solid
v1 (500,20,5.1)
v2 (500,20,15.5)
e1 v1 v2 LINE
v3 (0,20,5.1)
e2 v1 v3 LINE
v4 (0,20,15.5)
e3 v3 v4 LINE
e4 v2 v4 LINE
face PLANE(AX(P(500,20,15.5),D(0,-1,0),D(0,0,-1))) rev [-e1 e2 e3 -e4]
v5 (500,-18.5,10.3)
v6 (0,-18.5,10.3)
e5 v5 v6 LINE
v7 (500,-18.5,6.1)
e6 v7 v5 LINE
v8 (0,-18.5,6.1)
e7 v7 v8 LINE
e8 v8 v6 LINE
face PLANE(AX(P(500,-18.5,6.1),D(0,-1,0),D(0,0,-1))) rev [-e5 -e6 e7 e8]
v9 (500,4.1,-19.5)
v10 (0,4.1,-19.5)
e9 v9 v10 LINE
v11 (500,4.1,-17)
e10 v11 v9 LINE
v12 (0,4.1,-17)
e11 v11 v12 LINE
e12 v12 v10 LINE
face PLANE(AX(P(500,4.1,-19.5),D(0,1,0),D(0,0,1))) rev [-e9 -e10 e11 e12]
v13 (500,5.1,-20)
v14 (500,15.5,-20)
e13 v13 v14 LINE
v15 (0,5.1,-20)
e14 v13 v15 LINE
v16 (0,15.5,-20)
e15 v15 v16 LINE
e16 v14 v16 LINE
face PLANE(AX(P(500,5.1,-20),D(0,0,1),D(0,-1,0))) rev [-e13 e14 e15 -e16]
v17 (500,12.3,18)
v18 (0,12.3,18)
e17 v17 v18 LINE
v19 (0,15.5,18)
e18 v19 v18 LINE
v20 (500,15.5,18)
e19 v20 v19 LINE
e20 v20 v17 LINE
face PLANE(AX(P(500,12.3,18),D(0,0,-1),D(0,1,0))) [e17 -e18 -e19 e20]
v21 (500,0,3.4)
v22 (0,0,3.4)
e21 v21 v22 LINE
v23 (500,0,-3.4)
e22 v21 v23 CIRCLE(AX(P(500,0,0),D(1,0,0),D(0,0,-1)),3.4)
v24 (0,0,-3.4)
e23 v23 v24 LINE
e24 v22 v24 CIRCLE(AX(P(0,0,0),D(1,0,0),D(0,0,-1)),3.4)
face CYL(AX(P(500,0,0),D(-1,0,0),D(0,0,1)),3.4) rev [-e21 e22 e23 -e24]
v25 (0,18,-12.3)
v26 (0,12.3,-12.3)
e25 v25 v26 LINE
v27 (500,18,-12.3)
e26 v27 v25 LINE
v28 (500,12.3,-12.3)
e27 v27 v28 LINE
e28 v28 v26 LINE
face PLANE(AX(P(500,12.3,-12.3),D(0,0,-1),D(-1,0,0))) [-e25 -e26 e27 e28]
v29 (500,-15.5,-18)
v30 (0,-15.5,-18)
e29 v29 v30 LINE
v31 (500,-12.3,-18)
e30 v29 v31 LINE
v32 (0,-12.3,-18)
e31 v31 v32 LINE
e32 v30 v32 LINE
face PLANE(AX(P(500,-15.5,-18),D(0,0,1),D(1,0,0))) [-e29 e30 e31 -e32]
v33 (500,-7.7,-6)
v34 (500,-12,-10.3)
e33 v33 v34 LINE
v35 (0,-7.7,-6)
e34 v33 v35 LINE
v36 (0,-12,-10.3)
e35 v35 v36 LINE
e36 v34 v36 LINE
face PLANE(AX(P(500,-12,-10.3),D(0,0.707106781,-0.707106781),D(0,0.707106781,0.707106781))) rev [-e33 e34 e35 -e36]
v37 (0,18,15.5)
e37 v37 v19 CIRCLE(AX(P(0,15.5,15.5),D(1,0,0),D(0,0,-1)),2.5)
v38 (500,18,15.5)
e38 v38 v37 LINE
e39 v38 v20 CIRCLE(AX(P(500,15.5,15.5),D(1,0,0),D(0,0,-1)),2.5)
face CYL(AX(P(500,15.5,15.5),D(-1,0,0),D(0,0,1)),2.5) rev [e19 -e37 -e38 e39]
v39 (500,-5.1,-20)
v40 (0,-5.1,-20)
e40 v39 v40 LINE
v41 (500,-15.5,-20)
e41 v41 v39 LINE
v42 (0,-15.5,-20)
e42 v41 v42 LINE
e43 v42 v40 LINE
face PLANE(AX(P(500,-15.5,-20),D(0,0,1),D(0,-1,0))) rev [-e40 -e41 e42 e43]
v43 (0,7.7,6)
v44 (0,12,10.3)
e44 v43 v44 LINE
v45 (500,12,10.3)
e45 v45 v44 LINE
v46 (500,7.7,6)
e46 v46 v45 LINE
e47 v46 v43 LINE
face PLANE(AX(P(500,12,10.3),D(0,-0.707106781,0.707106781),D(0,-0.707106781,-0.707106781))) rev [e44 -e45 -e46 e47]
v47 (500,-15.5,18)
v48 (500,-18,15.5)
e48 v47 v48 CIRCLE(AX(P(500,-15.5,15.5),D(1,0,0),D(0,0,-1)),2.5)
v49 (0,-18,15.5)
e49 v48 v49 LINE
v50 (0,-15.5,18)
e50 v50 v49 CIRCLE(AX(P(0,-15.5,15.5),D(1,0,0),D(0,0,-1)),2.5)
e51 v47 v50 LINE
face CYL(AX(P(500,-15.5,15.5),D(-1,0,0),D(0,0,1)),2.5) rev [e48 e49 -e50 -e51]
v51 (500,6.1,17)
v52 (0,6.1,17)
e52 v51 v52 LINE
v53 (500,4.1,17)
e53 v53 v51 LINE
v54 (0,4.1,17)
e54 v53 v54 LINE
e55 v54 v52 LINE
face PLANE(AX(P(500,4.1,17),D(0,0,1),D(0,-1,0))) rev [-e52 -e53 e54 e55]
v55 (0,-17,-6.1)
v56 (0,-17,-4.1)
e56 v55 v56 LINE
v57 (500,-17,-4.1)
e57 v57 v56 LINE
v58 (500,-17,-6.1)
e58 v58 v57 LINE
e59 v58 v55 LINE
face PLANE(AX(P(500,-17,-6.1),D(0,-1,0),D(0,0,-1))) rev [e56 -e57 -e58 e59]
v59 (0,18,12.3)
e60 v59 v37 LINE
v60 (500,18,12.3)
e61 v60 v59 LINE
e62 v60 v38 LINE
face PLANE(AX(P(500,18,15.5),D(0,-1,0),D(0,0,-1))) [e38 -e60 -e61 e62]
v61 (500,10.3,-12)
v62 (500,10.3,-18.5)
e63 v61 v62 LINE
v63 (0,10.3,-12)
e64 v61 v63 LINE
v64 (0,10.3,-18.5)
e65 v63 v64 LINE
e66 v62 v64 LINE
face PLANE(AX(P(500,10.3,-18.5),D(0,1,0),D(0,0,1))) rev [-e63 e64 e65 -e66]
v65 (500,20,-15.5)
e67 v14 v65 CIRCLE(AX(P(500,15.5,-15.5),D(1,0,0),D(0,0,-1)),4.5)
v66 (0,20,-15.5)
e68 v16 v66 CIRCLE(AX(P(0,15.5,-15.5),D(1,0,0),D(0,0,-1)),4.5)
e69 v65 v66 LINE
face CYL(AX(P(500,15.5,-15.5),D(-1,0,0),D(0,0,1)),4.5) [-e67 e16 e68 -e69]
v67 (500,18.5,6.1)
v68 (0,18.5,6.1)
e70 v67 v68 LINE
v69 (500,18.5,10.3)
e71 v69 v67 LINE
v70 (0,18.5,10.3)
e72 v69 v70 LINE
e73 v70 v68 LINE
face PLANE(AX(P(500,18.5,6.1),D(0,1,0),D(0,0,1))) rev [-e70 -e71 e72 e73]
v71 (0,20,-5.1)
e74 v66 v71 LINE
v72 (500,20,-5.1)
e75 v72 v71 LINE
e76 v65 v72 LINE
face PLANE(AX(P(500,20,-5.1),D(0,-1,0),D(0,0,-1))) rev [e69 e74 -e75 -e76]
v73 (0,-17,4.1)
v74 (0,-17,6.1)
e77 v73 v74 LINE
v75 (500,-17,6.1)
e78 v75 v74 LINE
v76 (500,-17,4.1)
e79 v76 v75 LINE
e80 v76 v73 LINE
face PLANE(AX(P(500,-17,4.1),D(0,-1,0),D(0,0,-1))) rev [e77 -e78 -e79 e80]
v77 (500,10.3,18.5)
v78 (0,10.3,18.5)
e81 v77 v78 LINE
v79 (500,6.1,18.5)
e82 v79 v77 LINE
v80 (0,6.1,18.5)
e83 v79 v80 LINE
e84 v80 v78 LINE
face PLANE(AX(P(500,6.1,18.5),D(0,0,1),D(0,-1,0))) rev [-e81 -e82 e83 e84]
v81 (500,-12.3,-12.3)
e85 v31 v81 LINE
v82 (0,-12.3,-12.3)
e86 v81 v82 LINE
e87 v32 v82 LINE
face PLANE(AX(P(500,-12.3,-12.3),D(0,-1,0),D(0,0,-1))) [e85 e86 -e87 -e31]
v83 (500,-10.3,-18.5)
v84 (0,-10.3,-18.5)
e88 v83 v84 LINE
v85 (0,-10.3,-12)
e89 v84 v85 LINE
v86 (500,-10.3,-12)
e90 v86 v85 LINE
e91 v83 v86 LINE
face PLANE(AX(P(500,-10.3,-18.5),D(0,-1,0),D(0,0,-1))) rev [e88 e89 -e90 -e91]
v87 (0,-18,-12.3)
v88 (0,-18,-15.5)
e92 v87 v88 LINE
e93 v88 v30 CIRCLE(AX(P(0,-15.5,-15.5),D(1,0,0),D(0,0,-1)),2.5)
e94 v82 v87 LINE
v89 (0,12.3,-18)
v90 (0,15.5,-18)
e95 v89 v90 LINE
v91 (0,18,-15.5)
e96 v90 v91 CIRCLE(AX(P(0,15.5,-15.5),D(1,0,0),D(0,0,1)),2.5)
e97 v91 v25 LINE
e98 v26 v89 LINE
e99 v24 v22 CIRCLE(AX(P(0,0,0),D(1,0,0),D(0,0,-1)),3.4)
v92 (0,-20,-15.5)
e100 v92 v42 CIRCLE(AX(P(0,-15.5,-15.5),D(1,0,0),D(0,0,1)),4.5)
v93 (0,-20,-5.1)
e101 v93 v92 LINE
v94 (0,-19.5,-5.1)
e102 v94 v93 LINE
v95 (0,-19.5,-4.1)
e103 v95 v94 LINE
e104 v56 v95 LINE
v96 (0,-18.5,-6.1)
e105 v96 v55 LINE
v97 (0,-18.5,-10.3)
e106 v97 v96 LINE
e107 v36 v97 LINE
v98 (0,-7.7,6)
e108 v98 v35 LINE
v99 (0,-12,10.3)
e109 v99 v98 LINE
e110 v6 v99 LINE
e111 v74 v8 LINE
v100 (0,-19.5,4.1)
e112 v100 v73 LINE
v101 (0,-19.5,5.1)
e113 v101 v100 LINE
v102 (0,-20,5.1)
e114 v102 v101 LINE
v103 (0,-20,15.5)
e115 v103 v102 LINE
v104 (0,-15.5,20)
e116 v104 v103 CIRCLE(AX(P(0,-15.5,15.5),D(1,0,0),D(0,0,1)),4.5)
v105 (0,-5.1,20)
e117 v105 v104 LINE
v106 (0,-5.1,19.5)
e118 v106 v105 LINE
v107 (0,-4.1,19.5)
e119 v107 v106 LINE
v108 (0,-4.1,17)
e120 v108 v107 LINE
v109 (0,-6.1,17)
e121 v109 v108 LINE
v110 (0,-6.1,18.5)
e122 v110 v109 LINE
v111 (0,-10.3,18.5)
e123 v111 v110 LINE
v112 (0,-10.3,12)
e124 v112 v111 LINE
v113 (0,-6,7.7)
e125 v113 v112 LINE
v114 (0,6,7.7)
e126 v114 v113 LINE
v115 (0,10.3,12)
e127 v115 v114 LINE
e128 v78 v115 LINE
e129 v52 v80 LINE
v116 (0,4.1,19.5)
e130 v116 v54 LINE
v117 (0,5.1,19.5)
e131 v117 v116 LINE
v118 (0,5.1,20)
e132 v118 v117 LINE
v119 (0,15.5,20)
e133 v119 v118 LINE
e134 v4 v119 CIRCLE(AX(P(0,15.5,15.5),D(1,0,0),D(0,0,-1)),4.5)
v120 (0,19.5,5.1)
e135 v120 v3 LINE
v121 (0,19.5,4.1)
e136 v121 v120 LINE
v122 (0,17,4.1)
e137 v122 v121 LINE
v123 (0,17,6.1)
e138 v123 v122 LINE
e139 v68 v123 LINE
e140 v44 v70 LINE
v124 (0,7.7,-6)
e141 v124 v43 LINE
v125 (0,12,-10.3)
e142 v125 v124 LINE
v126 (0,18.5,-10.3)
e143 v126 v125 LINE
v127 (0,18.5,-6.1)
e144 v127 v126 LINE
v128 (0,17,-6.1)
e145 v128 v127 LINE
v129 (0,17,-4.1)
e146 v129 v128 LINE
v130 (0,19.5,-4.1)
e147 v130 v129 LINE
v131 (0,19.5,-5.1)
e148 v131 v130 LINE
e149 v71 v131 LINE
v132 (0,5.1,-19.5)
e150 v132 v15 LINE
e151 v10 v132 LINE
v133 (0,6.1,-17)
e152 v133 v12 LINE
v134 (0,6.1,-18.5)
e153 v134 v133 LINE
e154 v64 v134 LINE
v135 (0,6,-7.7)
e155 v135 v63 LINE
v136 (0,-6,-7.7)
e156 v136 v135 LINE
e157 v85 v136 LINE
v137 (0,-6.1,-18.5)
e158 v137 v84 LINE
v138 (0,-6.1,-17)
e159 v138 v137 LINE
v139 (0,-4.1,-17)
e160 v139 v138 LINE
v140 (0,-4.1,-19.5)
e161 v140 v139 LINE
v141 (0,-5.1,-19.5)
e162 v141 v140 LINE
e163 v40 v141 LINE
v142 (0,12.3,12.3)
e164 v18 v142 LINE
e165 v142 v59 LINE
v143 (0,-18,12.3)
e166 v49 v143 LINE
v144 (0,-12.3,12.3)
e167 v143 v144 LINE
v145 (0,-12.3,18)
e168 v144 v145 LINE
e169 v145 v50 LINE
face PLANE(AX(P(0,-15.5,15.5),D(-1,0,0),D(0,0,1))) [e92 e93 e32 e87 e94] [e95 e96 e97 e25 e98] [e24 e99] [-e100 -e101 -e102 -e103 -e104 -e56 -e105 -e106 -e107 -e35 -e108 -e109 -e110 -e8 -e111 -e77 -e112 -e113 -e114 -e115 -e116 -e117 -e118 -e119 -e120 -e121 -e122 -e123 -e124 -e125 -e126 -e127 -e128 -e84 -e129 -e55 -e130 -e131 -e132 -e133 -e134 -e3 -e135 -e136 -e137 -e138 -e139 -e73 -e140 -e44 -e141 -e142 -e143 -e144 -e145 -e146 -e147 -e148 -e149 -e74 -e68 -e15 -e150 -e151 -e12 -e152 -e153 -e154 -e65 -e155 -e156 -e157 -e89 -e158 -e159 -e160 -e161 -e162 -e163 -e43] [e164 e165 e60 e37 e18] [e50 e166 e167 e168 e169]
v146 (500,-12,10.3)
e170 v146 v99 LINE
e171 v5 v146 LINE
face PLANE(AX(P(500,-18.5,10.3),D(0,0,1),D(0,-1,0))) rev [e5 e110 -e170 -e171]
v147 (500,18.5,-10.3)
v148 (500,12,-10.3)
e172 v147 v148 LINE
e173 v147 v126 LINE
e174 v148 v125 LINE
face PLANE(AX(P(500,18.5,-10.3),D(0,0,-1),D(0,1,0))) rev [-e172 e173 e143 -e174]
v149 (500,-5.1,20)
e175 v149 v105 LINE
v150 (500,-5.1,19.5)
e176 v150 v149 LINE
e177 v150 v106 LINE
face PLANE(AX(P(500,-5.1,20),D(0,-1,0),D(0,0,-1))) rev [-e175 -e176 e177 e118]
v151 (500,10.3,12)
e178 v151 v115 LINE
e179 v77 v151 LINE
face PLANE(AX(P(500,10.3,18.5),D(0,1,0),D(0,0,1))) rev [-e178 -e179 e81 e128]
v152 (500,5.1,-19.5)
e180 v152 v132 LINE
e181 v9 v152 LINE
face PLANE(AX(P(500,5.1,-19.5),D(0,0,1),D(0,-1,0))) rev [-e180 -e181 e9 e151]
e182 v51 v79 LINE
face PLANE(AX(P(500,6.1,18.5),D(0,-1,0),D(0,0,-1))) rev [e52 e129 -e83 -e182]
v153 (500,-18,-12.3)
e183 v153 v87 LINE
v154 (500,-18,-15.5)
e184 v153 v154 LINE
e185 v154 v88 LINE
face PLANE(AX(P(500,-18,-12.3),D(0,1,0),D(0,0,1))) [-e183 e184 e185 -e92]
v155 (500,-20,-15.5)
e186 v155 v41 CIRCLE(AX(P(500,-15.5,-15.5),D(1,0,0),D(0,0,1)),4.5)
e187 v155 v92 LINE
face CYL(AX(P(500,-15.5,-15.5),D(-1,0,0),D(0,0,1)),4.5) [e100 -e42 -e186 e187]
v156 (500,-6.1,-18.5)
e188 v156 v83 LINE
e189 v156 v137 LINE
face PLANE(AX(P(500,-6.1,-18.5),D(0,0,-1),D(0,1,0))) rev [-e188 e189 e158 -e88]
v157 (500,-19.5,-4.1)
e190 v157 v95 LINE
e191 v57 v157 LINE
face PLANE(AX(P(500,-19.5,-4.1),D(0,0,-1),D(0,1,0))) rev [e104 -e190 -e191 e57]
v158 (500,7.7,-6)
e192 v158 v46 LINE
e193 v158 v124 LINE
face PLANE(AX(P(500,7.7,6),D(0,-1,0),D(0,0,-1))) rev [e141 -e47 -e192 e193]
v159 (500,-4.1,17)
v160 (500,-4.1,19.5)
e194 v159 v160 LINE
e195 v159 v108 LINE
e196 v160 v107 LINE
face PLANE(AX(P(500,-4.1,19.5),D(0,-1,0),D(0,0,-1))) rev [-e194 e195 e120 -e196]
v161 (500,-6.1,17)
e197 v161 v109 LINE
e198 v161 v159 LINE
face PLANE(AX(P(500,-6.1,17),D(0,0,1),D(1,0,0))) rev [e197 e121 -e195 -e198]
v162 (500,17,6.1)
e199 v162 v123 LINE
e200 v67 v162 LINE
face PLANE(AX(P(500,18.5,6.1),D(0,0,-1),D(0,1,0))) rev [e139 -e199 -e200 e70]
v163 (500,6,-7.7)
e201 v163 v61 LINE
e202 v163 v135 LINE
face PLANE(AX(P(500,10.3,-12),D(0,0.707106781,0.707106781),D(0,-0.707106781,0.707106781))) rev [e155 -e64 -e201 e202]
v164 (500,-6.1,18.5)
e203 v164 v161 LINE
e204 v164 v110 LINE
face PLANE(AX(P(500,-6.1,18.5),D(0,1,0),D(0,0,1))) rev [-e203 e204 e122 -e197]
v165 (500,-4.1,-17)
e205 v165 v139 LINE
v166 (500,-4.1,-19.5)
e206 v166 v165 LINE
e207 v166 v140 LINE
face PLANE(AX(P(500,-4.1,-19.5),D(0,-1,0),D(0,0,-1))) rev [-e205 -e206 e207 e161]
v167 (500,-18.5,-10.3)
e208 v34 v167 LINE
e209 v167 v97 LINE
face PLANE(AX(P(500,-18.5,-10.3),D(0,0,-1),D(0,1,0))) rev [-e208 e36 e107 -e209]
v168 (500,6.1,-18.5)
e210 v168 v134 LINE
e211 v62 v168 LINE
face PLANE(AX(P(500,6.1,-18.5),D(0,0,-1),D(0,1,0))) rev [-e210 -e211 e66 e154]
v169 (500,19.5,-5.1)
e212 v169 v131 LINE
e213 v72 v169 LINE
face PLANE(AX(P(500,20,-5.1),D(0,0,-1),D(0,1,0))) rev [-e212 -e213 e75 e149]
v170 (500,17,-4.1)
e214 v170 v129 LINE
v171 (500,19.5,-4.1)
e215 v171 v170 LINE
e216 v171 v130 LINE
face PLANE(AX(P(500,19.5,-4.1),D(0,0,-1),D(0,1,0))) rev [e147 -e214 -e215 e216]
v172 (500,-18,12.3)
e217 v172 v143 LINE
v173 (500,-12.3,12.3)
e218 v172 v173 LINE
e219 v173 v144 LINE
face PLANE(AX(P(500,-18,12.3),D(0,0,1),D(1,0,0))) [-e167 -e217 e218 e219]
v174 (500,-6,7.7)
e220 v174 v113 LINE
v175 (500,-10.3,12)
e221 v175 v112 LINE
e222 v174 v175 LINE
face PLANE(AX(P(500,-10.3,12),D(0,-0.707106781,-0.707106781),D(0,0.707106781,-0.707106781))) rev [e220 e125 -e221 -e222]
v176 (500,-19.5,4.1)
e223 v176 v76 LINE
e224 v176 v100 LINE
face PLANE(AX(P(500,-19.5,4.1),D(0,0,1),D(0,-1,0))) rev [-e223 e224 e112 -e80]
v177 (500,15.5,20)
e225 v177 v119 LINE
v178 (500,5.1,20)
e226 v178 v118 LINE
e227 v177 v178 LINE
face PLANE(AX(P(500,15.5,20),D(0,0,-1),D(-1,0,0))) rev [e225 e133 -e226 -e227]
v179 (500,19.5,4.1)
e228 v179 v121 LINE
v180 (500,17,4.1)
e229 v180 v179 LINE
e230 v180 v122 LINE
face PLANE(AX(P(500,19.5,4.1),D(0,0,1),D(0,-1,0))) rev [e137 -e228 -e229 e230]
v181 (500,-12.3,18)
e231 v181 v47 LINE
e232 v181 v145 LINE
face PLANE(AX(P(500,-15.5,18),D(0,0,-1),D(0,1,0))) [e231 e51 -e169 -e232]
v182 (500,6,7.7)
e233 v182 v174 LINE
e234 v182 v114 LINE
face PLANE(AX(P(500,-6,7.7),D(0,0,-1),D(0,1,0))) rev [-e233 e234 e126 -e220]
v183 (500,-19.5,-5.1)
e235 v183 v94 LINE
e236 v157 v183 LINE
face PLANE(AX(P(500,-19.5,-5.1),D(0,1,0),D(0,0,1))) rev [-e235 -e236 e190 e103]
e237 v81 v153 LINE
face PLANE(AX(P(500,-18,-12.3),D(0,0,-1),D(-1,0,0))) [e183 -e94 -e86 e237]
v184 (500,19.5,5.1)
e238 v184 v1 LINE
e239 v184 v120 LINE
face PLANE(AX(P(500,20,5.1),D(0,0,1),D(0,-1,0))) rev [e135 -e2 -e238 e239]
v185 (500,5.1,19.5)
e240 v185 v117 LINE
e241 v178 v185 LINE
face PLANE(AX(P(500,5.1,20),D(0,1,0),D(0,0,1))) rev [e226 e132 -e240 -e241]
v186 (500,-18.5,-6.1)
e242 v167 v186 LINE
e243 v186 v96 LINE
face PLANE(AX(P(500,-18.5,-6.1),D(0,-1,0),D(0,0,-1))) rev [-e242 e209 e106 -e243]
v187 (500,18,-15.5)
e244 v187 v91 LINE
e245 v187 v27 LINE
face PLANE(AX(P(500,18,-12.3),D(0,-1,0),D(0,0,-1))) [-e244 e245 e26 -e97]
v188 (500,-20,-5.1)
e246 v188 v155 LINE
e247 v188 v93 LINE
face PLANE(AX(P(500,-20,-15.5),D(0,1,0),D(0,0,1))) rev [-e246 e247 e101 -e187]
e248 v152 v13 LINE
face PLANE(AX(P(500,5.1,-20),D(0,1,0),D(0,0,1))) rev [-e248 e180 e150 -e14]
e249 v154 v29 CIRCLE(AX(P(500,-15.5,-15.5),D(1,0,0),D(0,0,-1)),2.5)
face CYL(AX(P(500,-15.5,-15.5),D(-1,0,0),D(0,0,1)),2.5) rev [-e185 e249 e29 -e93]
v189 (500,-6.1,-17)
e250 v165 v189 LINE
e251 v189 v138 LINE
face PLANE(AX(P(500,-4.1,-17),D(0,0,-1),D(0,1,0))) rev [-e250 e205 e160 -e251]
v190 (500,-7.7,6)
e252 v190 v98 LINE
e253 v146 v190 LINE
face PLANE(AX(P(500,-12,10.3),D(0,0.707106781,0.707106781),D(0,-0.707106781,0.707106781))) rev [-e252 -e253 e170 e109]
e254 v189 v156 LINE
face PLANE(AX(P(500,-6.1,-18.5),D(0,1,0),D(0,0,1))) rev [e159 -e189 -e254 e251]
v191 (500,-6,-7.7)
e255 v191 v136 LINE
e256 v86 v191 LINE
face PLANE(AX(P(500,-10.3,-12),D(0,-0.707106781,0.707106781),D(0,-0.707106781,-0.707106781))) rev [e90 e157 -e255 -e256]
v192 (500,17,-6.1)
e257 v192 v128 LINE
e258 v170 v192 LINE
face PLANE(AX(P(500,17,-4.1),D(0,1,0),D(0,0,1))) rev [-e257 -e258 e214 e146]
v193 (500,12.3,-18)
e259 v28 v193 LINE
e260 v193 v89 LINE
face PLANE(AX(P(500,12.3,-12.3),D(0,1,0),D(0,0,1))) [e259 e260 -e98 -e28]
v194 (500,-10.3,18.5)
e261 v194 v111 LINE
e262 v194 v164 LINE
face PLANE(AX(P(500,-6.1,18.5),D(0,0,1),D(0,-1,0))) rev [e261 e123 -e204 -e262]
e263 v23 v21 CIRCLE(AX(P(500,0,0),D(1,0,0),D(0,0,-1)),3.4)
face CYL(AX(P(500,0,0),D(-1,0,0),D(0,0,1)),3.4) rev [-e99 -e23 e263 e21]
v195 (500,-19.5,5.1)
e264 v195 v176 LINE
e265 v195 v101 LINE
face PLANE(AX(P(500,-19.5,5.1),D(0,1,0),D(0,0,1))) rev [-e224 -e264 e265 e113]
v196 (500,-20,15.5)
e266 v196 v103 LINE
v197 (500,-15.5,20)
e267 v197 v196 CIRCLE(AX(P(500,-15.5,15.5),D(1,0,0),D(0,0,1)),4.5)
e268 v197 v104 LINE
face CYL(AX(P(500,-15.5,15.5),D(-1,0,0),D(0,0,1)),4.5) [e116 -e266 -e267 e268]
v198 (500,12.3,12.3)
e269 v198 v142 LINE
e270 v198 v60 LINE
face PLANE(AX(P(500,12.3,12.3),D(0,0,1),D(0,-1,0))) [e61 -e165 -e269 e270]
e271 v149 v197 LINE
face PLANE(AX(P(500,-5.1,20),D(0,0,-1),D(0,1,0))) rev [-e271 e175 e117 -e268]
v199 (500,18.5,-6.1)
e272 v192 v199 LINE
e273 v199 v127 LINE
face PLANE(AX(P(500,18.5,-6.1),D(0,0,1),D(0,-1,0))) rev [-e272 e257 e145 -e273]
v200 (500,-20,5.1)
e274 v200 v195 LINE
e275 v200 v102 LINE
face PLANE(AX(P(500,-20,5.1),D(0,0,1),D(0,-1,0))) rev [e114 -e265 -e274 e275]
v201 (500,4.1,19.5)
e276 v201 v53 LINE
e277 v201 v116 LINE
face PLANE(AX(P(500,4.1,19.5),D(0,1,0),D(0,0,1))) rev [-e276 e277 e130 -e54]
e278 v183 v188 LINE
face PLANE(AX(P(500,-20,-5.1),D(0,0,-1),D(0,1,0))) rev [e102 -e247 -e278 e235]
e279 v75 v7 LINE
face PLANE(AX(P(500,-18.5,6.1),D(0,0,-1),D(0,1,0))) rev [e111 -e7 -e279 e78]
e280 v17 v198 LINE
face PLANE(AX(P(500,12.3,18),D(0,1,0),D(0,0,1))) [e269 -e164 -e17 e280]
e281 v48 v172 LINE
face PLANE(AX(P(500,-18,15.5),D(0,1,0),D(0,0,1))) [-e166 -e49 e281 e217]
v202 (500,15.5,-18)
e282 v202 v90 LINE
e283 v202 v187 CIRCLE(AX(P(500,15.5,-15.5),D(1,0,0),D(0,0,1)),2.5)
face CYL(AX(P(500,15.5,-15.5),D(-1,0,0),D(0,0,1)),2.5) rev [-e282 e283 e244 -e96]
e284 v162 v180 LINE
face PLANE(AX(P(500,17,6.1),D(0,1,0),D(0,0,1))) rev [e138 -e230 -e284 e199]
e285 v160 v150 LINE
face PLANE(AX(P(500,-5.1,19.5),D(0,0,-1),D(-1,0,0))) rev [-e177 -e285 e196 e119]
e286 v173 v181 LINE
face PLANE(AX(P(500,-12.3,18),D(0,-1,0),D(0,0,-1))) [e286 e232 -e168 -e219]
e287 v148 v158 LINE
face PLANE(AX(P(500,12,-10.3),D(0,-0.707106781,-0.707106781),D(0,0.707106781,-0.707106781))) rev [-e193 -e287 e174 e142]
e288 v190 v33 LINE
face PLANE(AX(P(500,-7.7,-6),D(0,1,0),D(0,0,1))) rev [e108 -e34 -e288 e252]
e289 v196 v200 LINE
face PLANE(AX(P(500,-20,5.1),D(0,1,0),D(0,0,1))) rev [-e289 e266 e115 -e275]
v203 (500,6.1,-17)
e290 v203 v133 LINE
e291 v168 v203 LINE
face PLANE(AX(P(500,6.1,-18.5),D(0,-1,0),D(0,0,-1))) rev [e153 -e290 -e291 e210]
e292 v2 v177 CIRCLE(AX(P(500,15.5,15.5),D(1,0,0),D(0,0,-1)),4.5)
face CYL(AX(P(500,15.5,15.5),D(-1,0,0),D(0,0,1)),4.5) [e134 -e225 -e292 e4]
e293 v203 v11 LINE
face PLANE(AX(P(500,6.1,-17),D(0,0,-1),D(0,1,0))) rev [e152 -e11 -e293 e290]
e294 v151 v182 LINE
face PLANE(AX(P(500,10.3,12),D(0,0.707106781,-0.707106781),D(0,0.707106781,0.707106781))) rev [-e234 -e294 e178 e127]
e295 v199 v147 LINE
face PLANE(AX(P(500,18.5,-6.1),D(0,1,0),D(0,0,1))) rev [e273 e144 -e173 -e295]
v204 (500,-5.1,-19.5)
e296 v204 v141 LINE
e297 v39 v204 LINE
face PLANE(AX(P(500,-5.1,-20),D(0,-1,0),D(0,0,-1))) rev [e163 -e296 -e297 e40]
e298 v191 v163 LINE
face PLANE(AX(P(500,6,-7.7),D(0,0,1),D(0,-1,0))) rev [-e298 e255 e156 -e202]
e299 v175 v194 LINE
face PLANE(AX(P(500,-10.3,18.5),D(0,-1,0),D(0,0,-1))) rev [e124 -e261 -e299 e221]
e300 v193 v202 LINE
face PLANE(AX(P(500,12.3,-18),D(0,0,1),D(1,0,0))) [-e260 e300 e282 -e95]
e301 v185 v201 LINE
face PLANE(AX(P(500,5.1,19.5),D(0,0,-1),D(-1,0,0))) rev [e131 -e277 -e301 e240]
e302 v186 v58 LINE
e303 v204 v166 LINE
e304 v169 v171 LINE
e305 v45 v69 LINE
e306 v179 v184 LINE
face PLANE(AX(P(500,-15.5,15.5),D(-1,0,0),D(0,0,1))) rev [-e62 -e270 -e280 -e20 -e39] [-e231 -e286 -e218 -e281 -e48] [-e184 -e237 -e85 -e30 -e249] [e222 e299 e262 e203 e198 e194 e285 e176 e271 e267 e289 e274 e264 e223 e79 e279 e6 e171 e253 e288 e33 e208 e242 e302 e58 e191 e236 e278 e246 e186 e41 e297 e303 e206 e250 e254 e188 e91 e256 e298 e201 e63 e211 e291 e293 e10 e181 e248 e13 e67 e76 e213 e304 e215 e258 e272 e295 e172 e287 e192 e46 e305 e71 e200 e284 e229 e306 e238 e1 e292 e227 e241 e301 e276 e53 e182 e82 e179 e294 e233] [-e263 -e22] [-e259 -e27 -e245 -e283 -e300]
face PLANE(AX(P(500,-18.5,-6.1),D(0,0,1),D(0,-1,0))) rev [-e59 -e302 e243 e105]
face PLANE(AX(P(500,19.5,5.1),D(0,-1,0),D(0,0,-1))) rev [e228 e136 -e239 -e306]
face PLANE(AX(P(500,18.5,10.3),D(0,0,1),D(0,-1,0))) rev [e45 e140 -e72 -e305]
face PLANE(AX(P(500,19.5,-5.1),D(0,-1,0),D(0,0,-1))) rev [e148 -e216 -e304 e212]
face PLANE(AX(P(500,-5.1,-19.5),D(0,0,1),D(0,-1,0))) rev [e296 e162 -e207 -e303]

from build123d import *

# Parameters (mm, degrees)
SKETCH1_R                                = 3.4
ALUMINUM_PROFILE_40_X_40B_X_R4_5_1_DEPTH = 500


with BuildPart() as part:
    # Sketch1 → Aluminum profile 40 X 40B X R4.5(1) (new body)
    with BuildSketch(Plane.YZ):
        with BuildLine():
            Line((-5.1, 20), (-5.1, 19.5))
            Line((-5.1, 19.5), (-4.1, 19.5))
            Line((-4.1, 19.5), (-4.1, 17))
            Line((-4.1, 17), (-6.1, 17))
            Line((-6.1, 17), (-6.1, 18.5))
            Line((-6.1, 18.5), (-10.3, 18.5))
            Line((-10.3, 18.5), (-10.3, 12))
            Line((-10.3, 12), (-6, 7.7))
            Line((-6, 7.7), (6, 7.7))
            Line((6, 7.7), (10.3, 12))
            Line((10.3, 12), (10.3, 18.5))
            Line((10.3, 18.5), (6.1, 18.5))
            Line((6.1, 18.5), (6.1, 17))
            Line((6.1, 17), (4.1, 17))
            Line((4.1, 17), (4.1, 19.5))
            Line((4.1, 19.5), (5.1, 19.5))
            Line((5.1, 19.5), (5.1, 20))
            Line((5.1, 20), (15.5, 20))
            ThreePointArc((15.5, 20), (18.681980515, 18.681980515), (20, 15.5))
            Line((20, 15.5), (20, 5.1))
            Line((20, 5.1), (19.5, 5.1))
            Line((19.5, 5.1), (19.5, 4.1))
            Line((19.5, 4.1), (17, 4.1))
            Line((17, 4.1), (17, 6.1))
            Line((17, 6.1), (18.5, 6.1))
            Line((18.5, 6.1), (18.5, 10.3))
            Line((18.5, 10.3), (12, 10.3))
            Line((12, 10.3), (7.7, 6))
            Line((7.7, 6), (7.7, -6))
            Line((7.7, -6), (12, -10.3))
            Line((12, -10.3), (18.5, -10.3))
            Line((18.5, -10.3), (18.5, -6.1))
            Line((18.5, -6.1), (17, -6.1))
            Line((17, -6.1), (17, -4.1))
            Line((17, -4.1), (19.5, -4.1))
            Line((19.5, -4.1), (19.5, -5.1))
            Line((19.5, -5.1), (20, -5.1))
            Line((20, -5.1), (20, -15.5))
            ThreePointArc((20, -15.5), (18.681980515, -18.681980515), (15.5, -20))
            Line((15.5, -20), (5.1, -20))
            Line((5.1, -20), (5.1, -19.5))
            Line((5.1, -19.5), (4.1, -19.5))
            Line((4.1, -19.5), (4.1, -17))
            Line((4.1, -17), (6.1, -17))
            Line((6.1, -17), (6.1, -18.5))
            Line((6.1, -18.5), (10.3, -18.5))
            Line((10.3, -18.5), (10.3, -12))
            Line((10.3, -12), (6, -7.7))
            Line((6, -7.7), (-6, -7.7))
            Line((-6, -7.7), (-10.3, -12))
            Line((-10.3, -12), (-10.3, -18.5))
            Line((-10.3, -18.5), (-6.1, -18.5))
            Line((-6.1, -18.5), (-6.1, -17))
            Line((-6.1, -17), (-4.1, -17))
            Line((-4.1, -17), (-4.1, -19.5))
            Line((-4.1, -19.5), (-5.1, -19.5))
            Line((-5.1, -19.5), (-5.1, -20))
            Line((-5.1, -20), (-15.5, -20))
            ThreePointArc((-15.5, -20), (-18.681980515, -18.681980515), (-20, -15.5))
            Line((-20, -15.5), (-20, -5.1))
            Line((-20, -5.1), (-19.5, -5.1))
            Line((-19.5, -5.1), (-19.5, -4.1))
            Line((-19.5, -4.1), (-17, -4.1))
            Line((-17, -4.1), (-17, -6.1))
            Line((-17, -6.1), (-18.5, -6.1))
            Line((-18.5, -6.1), (-18.5, -10.3))
            Line((-18.5, -10.3), (-12, -10.3))
            Line((-12, -10.3), (-7.7, -6))
            Line((-7.7, -6), (-7.7, 6))
            Line((-7.7, 6), (-12, 10.3))
            Line((-12, 10.3), (-18.5, 10.3))
            Line((-18.5, 10.3), (-18.5, 6.1))
            Line((-18.5, 6.1), (-17, 6.1))
            Line((-17, 6.1), (-17, 4.1))
            Line((-17, 4.1), (-19.5, 4.1))
            Line((-19.5, 4.1), (-19.5, 5.1))
            Line((-19.5, 5.1), (-20, 5.1))
            Line((-20, 5.1), (-20, 15.5))
            ThreePointArc((-20, 15.5), (-18.681980515, 18.681980515), (-15.5, 20))
            Line((-15.5, 20), (-5.1, 20))
        make_face()
        Circle(SKETCH1_R, mode=Mode.SUBTRACT)
        with BuildLine():
            Line((12.3, 18), (15.5, 18))
            ThreePointArc((15.5, 18), (17.267766953, 17.267766953), (18, 15.5))
            Line((18, 15.5), (18, 12.3))
            Line((18, 12.3), (12.3, 12.3))
            Line((12.3, 12.3), (12.3, 18))
        make_face(mode=Mode.SUBTRACT)
        with BuildLine():
            Line((-15.5, 18), (-12.3, 18))
            Line((-12.3, 18), (-12.3, 12.3))
            Line((-12.3, 12.3), (-18, 12.3))
            Line((-18, 12.3), (-18, 15.5))
            ThreePointArc((-18, 15.5), (-17.267766953, 17.267766953), (-15.5, 18))
        make_face(mode=Mode.SUBTRACT)
        with BuildLine():
            Line((-18, -12.3), (-12.3, -12.3))
            Line((-12.3, -12.3), (-12.3, -18))
            Line((-12.3, -18), (-15.5, -18))
            ThreePointArc((-15.5, -18), (-17.267766953, -17.267766953), (-18, -15.5))
            Line((-18, -15.5), (-18, -12.3))
        make_face(mode=Mode.SUBTRACT)
        with BuildLine():
            Line((12.3, -12.3), (18, -12.3))
            Line((18, -12.3), (18, -15.5))
            ThreePointArc((18, -15.5), (17.267766953, -17.267766953), (15.5, -18))
            Line((15.5, -18), (12.3, -18))
            Line((12.3, -18), (12.3, -12.3))
        make_face(mode=Mode.SUBTRACT)
    extrude(amount=ALUMINUM_PROFILE_40_X_40B_X_R4_5_1_DEPTH)


solid = part.part
